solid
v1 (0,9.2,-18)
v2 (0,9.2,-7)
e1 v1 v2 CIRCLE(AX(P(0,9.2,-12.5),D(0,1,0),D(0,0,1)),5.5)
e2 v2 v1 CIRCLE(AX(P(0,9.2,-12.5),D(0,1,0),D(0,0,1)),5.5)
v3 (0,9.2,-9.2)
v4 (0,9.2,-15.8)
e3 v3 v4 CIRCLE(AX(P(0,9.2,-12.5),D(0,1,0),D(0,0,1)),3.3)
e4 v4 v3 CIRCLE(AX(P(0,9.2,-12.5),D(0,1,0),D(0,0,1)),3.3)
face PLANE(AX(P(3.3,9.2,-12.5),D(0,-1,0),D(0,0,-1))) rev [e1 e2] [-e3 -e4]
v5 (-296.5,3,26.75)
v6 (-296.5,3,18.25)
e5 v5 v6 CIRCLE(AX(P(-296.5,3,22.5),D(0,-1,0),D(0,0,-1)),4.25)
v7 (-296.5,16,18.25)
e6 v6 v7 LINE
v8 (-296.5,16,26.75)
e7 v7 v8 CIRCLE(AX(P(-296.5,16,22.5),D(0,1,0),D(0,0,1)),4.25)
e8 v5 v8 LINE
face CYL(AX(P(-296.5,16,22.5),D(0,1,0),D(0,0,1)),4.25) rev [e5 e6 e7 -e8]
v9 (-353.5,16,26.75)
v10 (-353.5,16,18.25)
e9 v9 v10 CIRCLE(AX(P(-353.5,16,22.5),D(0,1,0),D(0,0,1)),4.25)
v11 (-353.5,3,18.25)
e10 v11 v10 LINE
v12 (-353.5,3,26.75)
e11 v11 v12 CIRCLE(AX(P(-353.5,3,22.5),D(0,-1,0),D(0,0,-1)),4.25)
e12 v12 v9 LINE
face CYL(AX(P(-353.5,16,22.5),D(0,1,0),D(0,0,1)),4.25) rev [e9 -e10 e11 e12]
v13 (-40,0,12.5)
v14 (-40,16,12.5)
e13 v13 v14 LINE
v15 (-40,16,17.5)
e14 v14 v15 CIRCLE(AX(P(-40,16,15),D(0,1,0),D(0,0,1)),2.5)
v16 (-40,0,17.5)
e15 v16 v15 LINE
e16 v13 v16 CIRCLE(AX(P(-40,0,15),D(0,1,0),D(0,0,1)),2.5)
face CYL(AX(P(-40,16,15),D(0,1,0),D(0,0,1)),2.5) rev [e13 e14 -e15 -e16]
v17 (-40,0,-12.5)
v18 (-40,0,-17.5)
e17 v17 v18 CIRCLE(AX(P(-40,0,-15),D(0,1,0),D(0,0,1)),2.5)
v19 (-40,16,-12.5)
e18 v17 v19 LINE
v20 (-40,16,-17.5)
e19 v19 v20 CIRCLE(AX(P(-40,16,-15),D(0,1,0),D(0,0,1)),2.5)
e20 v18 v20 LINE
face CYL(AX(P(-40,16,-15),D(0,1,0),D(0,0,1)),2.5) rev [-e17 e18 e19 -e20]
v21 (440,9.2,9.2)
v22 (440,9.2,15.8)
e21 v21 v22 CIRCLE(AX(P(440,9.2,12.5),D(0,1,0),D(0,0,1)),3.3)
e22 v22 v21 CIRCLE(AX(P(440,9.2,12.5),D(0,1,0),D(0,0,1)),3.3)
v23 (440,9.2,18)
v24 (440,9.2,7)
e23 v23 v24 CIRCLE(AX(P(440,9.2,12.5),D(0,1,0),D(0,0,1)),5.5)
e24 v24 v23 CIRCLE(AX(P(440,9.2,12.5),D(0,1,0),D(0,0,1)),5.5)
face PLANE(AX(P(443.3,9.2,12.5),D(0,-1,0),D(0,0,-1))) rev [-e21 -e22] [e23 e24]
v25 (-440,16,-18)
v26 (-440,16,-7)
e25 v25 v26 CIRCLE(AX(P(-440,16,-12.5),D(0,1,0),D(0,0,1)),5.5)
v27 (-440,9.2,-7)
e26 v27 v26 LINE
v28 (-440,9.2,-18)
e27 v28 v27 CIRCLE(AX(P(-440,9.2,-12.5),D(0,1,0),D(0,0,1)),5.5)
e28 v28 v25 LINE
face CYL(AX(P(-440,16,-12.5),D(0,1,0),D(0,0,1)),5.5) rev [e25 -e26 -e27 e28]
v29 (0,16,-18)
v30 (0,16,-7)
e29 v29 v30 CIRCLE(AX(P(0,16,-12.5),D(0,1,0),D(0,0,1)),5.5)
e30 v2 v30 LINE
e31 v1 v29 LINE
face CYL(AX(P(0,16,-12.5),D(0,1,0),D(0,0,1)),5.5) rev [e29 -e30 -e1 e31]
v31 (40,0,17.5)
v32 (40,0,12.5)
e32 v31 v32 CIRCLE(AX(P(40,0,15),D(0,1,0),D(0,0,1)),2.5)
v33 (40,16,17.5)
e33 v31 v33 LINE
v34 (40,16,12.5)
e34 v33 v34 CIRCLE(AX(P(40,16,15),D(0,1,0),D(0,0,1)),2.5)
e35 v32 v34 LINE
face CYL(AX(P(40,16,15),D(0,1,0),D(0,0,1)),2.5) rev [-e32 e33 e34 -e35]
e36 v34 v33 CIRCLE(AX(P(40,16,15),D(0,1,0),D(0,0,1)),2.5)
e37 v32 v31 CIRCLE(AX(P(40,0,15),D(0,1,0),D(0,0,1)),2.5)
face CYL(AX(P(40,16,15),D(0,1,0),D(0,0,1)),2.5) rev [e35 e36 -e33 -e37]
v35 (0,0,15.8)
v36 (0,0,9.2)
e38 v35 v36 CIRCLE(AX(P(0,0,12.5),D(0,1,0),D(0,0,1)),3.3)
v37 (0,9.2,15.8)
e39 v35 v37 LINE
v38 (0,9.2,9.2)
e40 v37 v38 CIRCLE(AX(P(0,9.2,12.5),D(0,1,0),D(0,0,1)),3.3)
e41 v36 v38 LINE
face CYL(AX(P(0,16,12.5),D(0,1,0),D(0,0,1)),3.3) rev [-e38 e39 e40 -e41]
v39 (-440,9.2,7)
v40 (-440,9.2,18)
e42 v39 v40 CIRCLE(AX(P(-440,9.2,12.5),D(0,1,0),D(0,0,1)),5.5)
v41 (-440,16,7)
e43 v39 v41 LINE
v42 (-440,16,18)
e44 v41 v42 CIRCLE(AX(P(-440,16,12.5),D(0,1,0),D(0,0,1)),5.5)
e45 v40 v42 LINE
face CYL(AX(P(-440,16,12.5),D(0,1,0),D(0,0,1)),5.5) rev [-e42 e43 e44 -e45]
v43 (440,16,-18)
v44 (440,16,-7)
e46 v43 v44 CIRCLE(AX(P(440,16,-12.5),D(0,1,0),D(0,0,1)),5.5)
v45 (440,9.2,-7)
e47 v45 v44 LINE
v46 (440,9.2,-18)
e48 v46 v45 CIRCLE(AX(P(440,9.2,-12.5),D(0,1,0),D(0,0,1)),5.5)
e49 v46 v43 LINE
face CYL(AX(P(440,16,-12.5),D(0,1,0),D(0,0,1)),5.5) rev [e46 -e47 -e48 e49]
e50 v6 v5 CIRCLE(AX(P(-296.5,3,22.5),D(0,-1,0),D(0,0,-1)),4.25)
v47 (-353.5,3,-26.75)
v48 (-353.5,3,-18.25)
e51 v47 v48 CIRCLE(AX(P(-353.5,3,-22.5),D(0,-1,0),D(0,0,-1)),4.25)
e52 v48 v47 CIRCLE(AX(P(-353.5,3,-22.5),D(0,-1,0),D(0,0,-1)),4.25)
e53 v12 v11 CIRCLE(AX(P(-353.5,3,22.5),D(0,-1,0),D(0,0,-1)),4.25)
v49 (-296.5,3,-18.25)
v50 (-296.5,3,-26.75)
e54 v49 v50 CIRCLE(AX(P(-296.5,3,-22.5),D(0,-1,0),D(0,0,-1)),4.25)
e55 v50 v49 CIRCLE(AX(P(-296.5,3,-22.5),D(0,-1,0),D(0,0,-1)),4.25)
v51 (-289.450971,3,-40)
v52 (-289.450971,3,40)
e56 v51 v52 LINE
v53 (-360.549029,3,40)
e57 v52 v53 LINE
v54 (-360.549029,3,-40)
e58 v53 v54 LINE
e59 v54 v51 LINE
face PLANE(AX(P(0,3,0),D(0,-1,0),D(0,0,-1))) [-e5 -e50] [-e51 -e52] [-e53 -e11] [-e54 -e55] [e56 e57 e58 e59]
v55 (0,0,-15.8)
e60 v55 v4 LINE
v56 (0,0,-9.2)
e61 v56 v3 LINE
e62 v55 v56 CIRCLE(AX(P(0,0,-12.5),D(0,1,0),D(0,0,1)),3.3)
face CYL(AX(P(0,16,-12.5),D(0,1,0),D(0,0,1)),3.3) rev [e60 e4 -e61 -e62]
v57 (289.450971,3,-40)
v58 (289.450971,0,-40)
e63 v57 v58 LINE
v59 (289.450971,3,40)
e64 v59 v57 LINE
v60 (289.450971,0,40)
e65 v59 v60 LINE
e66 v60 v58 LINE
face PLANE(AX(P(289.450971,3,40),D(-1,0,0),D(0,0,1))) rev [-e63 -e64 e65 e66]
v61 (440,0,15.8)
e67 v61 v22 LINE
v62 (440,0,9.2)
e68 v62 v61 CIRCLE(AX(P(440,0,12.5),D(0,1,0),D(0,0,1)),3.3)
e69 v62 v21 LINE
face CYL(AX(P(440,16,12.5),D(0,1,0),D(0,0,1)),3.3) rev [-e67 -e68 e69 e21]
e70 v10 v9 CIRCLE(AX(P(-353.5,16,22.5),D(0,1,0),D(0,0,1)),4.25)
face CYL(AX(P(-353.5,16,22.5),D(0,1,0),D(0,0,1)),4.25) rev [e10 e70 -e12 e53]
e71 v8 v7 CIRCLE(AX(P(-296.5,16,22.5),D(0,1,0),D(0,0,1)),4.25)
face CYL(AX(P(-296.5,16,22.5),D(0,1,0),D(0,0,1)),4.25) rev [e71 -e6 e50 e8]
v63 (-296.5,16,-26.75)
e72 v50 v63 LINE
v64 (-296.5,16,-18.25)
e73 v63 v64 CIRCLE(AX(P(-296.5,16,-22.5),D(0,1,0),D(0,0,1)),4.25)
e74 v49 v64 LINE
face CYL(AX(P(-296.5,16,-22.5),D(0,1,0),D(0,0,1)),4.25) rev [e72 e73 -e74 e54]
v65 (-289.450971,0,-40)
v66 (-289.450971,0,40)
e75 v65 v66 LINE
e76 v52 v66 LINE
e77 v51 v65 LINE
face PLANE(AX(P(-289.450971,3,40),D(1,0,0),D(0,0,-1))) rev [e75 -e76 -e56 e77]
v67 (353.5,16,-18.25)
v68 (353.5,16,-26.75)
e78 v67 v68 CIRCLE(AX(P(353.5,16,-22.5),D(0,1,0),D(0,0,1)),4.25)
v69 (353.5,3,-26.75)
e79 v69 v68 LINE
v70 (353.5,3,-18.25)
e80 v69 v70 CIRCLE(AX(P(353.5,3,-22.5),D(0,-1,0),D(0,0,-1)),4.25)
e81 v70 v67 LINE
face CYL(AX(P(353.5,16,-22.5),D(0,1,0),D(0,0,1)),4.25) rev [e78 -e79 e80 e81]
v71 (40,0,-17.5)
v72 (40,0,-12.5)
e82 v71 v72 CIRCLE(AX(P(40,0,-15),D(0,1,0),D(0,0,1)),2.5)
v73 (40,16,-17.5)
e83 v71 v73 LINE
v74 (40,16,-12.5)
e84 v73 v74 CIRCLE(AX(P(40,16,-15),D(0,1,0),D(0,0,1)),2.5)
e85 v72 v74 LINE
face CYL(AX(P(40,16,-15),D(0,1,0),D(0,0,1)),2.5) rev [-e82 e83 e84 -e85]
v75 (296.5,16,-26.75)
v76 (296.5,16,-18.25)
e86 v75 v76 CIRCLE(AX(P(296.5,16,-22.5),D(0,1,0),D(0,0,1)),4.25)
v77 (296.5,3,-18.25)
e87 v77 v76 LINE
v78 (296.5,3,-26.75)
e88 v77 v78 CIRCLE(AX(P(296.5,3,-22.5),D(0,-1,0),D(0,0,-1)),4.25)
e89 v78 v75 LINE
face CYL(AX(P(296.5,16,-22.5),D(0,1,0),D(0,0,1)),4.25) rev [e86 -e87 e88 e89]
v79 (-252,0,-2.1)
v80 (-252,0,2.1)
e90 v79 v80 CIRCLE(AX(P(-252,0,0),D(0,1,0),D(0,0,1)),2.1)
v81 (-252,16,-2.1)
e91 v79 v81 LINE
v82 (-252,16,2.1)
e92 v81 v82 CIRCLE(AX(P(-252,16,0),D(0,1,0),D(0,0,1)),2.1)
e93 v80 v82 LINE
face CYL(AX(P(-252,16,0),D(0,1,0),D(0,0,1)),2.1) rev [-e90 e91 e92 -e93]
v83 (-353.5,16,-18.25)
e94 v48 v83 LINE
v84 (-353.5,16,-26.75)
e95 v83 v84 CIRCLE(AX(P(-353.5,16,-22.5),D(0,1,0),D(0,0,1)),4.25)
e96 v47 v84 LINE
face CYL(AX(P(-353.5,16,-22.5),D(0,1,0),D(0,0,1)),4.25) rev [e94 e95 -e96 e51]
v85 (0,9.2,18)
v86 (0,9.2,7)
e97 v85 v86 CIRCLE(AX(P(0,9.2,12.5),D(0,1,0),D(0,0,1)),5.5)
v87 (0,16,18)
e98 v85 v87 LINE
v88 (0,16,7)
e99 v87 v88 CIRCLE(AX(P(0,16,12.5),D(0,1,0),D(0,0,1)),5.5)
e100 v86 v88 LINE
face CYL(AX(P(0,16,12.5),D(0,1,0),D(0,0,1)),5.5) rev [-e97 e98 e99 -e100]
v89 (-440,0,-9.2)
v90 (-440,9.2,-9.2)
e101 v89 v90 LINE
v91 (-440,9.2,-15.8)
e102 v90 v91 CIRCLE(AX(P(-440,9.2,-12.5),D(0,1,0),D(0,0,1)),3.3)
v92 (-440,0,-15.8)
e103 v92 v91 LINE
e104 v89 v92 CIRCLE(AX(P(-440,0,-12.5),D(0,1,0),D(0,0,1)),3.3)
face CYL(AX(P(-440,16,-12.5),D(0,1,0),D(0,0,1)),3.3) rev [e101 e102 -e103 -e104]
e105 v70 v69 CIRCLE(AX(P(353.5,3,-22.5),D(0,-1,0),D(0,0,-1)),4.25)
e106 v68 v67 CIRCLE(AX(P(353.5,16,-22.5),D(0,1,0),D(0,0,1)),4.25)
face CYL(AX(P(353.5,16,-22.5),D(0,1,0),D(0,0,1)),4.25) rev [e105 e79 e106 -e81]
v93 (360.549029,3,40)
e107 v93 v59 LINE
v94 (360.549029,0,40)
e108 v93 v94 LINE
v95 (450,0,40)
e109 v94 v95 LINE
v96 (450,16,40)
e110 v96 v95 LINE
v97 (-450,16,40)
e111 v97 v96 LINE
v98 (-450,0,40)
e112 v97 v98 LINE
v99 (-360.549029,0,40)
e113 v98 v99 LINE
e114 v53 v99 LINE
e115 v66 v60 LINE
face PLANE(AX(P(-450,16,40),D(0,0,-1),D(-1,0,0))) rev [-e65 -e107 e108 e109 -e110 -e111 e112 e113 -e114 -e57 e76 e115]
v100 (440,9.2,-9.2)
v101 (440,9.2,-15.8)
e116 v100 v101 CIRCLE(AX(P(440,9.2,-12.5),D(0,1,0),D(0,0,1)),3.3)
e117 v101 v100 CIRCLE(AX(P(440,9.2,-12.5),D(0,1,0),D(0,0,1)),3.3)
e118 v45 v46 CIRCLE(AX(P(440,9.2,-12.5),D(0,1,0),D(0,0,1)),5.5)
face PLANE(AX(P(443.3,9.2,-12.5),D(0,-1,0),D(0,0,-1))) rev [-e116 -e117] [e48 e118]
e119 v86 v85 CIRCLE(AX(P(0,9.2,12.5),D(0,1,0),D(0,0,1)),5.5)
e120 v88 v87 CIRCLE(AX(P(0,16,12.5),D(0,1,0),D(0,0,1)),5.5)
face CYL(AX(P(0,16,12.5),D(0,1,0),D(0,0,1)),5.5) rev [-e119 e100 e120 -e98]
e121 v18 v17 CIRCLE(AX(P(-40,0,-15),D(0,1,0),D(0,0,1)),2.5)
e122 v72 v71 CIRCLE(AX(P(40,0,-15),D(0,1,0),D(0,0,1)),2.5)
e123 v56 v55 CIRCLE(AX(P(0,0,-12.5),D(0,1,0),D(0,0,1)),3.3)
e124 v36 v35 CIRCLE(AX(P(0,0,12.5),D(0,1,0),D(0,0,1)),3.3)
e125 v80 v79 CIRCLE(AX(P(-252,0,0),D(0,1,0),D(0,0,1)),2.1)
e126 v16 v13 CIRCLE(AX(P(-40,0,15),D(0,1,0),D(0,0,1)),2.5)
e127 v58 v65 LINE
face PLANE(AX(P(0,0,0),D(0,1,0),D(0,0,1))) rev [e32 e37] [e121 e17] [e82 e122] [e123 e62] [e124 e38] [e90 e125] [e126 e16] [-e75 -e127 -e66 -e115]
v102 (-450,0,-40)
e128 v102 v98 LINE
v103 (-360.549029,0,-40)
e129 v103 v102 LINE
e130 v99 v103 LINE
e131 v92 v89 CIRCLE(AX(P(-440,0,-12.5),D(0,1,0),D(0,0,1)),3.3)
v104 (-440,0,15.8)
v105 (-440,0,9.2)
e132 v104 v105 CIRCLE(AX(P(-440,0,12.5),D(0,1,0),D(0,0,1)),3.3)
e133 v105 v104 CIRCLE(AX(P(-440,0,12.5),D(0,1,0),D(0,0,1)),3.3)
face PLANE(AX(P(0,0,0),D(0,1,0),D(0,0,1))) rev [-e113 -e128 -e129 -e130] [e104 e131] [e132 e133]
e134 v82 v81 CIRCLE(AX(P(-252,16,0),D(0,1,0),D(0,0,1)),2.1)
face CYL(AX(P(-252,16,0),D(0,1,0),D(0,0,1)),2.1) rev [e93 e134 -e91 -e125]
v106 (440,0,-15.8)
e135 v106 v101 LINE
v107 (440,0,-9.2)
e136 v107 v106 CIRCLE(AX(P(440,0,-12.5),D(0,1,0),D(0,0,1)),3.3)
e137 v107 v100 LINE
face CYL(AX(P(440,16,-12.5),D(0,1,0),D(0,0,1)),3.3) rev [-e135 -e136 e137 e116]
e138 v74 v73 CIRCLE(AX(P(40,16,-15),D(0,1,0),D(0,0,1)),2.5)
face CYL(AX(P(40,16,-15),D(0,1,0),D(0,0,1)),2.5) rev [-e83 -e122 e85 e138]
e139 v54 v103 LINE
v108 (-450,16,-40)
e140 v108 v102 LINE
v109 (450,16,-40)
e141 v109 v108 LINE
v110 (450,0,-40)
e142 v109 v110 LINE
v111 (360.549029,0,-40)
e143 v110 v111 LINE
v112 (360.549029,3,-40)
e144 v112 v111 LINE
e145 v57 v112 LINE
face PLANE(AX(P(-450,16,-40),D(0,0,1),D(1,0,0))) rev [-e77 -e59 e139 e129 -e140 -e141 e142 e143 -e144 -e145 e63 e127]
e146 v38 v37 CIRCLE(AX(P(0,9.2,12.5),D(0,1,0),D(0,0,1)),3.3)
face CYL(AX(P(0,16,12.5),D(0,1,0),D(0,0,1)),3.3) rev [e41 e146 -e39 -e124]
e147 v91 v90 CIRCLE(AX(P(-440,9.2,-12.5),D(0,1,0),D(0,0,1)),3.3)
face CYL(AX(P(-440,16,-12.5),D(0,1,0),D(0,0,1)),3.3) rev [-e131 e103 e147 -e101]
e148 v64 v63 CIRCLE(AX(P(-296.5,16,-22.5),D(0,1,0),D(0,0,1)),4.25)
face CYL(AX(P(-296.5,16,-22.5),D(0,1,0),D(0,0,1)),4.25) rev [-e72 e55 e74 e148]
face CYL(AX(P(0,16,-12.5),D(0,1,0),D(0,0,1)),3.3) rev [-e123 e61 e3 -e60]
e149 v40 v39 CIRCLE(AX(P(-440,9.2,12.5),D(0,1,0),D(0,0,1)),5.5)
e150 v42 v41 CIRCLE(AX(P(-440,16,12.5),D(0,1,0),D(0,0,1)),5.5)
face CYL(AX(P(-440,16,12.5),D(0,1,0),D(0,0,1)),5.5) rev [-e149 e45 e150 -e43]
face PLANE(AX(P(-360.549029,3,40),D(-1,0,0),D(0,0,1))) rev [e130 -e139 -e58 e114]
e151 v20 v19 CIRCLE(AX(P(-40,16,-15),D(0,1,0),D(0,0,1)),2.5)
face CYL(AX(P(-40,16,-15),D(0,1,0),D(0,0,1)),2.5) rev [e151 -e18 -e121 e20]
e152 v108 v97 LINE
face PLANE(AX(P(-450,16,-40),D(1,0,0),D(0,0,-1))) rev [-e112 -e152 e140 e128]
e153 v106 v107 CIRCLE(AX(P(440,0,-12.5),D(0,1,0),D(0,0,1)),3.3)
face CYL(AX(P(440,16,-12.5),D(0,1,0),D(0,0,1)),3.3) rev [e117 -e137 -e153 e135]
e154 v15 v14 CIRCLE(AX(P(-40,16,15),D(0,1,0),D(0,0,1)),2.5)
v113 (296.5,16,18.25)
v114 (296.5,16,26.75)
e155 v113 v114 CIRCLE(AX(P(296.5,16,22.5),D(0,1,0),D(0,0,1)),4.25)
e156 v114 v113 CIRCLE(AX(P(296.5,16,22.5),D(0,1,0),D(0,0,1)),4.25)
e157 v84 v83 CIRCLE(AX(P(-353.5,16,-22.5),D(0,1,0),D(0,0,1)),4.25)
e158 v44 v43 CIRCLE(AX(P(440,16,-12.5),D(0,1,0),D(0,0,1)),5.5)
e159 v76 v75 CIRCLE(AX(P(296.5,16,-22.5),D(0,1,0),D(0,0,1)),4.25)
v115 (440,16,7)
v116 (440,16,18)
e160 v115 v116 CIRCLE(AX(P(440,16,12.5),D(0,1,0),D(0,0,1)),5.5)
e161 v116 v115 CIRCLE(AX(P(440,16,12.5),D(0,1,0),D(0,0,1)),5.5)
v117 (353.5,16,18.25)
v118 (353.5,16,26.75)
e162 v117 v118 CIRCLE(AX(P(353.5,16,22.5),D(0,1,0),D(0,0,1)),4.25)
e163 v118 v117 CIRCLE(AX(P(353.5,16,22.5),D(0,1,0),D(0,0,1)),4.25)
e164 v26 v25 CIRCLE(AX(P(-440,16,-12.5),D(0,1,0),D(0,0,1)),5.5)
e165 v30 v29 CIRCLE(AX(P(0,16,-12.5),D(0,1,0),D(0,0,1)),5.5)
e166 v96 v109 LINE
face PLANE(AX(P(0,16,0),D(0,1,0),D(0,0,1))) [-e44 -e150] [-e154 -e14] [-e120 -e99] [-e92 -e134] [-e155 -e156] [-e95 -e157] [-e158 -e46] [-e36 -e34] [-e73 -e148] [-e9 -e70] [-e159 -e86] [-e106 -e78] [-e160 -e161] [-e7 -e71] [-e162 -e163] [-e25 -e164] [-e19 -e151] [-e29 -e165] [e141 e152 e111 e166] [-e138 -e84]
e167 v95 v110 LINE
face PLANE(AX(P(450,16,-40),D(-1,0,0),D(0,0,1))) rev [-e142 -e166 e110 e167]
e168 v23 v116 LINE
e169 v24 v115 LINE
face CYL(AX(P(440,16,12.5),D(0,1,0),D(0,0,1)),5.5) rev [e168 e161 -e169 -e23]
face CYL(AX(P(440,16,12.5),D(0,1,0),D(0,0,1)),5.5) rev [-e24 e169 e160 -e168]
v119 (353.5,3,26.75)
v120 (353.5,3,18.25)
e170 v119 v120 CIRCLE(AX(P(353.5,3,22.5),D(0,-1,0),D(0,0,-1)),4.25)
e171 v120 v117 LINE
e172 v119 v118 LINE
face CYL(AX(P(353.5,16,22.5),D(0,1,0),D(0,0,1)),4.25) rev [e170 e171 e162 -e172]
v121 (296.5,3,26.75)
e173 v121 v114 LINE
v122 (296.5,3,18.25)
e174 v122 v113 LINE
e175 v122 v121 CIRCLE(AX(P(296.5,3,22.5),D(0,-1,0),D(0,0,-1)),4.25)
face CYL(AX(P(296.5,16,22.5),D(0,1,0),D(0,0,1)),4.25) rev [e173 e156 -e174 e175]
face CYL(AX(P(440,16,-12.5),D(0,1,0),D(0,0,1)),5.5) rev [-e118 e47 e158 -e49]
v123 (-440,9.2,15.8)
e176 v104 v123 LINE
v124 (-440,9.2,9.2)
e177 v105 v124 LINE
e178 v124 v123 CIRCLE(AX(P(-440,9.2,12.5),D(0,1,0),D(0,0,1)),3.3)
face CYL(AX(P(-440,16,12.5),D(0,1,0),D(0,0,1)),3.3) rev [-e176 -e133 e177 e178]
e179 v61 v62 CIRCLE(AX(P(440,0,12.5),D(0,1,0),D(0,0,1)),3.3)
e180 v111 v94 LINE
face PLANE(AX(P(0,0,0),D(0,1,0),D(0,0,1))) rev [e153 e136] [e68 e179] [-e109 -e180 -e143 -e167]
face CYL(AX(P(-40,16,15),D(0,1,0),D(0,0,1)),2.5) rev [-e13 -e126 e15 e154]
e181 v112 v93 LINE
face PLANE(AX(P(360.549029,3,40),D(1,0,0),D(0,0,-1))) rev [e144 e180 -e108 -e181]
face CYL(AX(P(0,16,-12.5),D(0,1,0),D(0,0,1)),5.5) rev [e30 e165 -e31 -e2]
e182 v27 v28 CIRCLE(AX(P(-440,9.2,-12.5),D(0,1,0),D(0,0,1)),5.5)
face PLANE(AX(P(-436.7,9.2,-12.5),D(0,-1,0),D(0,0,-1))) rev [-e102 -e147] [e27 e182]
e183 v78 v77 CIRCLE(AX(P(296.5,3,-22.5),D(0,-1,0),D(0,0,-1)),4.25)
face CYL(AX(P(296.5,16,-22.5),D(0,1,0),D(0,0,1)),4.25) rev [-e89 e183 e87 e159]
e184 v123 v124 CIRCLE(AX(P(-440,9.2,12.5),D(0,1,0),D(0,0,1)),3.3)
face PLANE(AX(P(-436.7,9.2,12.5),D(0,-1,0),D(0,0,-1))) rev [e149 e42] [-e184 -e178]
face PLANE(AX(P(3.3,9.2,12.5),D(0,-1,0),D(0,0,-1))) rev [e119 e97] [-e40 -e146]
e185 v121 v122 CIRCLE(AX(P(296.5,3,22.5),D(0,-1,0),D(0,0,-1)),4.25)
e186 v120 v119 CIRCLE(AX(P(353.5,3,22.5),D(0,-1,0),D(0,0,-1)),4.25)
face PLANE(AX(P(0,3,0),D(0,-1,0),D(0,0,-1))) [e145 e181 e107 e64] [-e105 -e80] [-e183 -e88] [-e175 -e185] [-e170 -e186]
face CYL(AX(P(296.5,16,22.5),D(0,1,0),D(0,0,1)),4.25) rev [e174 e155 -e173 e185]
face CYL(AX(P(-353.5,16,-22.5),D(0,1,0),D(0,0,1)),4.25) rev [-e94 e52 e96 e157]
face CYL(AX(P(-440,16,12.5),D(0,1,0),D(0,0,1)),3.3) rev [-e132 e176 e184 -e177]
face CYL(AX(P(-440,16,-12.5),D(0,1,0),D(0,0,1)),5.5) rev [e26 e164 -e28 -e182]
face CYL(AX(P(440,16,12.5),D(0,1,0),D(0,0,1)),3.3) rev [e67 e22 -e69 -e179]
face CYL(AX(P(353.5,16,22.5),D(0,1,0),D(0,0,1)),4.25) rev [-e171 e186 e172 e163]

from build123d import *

# Parameters (mm, degrees)
SKETCH_1_W                = 900
SKETCH_1_H                = 80
EXTRUDE_1_DEPTH           = 16
SKETCH_2_W                = 71.098057304
SKETCH_2_H                = 80
CUT_EXTRUDE_1_DEPTH       = 3
HOLE_WIZARD_8_5_8_5_1_D   = 8.5
HOLE_WIZARD_M6_1_D        = 5
HOLE_WIZARD_1_D           = 6.6
HOLE_WIZARD_1_CBORE_D     = 11
HOLE_WIZARD_1_CBORE_DEPTH = 6.8
PATTERN_LINEAR_1_COUNT    = 3
PATTERN_LINEAR_1_PITCH    = 440
HOLE_WIZARD_M5_1_D        = 4.2


with BuildPart() as part:
    # 草图1 → 凸台-拉伸1 (new body)
    with BuildSketch(Plane(origin=(0, 0, 0), x_dir=(1, 0, 0), z_dir=(0, 1, 0))):
        Rectangle(SKETCH_1_W, SKETCH_1_H)
    extrude(amount=EXTRUDE_1_DEPTH)

    # 草图2 → 切除-拉伸1 (cut)
    with BuildSketch(Plane.XZ):
        with Locations((-325, 0)):
            Rectangle(SKETCH_2_W, SKETCH_2_H)
        with Locations((325, 0)):
            Rectangle(SKETCH_2_W, SKETCH_2_H)
    extrude(amount=-CUT_EXTRUDE_1_DEPTH, mode=Mode.SUBTRACT)

    # Ø8.5 (8.5) 直径孔1 (through all)
    with Locations(Plane(origin=(0, 16, 0), x_dir=(1, 0, 0), z_dir=(0, 1, 0))):
        with Locations((-353.5, 22.5), (-296.5, 22.5), (-353.5, -22.5), (-296.5, -22.5)):
            hole_wizard_8_5_8_5_1 = Hole(HOLE_WIZARD_8_5_8_5_1_D / 2)

    # 镜向1: Ø8.5 (8.5) 直径孔1 across plane
    add(hole_wizard_8_5_8_5_1.mirror(Plane(origin=(0, 0, 0), x_dir=(0, 0, 1), z_dir=(1, 0, 0))), mode=Mode.SUBTRACT)

    # M6 螺纹孔1 (through all)
    with Locations(Plane(origin=(0, 16, 0), x_dir=(1, 0, 0), z_dir=(0, 1, 0))):
        with Locations((-40, 15), (40, 15), (-40, -15), (40, -15)):
            Hole(HOLE_WIZARD_M6_1_D / 2)

    # 打孔尺寸(%根据)内六角圆柱头螺钉的类型1 (through all)
    with Locations(Plane(origin=(0, 16, 0), x_dir=(1, 0, 0), z_dir=(0, 1, 0))):
        with Locations((-440, 12.5), (-440, -12.5)):
            hole_wizard_1 = CounterBoreHole(HOLE_WIZARD_1_D / 2, HOLE_WIZARD_1_CBORE_D / 2, HOLE_WIZARD_1_CBORE_DEPTH)

    # 阵列(线性)1: 打孔尺寸(%根据)内六角圆柱头螺钉的类型1 ×3
    with Locations(*[(i * PATTERN_LINEAR_1_PITCH, 0, 0) for i in range(1, PATTERN_LINEAR_1_COUNT)]):
        add(hole_wizard_1, mode=Mode.SUBTRACT)

    # M5 螺纹孔1 (through all)
    with Locations(Plane(origin=(0, 16, 0), x_dir=(1, 0, 0), z_dir=(0, 1, 0))):
        with Locations((-252, 0)):
            Hole(HOLE_WIZARD_M5_1_D / 2)


solid = part.part
